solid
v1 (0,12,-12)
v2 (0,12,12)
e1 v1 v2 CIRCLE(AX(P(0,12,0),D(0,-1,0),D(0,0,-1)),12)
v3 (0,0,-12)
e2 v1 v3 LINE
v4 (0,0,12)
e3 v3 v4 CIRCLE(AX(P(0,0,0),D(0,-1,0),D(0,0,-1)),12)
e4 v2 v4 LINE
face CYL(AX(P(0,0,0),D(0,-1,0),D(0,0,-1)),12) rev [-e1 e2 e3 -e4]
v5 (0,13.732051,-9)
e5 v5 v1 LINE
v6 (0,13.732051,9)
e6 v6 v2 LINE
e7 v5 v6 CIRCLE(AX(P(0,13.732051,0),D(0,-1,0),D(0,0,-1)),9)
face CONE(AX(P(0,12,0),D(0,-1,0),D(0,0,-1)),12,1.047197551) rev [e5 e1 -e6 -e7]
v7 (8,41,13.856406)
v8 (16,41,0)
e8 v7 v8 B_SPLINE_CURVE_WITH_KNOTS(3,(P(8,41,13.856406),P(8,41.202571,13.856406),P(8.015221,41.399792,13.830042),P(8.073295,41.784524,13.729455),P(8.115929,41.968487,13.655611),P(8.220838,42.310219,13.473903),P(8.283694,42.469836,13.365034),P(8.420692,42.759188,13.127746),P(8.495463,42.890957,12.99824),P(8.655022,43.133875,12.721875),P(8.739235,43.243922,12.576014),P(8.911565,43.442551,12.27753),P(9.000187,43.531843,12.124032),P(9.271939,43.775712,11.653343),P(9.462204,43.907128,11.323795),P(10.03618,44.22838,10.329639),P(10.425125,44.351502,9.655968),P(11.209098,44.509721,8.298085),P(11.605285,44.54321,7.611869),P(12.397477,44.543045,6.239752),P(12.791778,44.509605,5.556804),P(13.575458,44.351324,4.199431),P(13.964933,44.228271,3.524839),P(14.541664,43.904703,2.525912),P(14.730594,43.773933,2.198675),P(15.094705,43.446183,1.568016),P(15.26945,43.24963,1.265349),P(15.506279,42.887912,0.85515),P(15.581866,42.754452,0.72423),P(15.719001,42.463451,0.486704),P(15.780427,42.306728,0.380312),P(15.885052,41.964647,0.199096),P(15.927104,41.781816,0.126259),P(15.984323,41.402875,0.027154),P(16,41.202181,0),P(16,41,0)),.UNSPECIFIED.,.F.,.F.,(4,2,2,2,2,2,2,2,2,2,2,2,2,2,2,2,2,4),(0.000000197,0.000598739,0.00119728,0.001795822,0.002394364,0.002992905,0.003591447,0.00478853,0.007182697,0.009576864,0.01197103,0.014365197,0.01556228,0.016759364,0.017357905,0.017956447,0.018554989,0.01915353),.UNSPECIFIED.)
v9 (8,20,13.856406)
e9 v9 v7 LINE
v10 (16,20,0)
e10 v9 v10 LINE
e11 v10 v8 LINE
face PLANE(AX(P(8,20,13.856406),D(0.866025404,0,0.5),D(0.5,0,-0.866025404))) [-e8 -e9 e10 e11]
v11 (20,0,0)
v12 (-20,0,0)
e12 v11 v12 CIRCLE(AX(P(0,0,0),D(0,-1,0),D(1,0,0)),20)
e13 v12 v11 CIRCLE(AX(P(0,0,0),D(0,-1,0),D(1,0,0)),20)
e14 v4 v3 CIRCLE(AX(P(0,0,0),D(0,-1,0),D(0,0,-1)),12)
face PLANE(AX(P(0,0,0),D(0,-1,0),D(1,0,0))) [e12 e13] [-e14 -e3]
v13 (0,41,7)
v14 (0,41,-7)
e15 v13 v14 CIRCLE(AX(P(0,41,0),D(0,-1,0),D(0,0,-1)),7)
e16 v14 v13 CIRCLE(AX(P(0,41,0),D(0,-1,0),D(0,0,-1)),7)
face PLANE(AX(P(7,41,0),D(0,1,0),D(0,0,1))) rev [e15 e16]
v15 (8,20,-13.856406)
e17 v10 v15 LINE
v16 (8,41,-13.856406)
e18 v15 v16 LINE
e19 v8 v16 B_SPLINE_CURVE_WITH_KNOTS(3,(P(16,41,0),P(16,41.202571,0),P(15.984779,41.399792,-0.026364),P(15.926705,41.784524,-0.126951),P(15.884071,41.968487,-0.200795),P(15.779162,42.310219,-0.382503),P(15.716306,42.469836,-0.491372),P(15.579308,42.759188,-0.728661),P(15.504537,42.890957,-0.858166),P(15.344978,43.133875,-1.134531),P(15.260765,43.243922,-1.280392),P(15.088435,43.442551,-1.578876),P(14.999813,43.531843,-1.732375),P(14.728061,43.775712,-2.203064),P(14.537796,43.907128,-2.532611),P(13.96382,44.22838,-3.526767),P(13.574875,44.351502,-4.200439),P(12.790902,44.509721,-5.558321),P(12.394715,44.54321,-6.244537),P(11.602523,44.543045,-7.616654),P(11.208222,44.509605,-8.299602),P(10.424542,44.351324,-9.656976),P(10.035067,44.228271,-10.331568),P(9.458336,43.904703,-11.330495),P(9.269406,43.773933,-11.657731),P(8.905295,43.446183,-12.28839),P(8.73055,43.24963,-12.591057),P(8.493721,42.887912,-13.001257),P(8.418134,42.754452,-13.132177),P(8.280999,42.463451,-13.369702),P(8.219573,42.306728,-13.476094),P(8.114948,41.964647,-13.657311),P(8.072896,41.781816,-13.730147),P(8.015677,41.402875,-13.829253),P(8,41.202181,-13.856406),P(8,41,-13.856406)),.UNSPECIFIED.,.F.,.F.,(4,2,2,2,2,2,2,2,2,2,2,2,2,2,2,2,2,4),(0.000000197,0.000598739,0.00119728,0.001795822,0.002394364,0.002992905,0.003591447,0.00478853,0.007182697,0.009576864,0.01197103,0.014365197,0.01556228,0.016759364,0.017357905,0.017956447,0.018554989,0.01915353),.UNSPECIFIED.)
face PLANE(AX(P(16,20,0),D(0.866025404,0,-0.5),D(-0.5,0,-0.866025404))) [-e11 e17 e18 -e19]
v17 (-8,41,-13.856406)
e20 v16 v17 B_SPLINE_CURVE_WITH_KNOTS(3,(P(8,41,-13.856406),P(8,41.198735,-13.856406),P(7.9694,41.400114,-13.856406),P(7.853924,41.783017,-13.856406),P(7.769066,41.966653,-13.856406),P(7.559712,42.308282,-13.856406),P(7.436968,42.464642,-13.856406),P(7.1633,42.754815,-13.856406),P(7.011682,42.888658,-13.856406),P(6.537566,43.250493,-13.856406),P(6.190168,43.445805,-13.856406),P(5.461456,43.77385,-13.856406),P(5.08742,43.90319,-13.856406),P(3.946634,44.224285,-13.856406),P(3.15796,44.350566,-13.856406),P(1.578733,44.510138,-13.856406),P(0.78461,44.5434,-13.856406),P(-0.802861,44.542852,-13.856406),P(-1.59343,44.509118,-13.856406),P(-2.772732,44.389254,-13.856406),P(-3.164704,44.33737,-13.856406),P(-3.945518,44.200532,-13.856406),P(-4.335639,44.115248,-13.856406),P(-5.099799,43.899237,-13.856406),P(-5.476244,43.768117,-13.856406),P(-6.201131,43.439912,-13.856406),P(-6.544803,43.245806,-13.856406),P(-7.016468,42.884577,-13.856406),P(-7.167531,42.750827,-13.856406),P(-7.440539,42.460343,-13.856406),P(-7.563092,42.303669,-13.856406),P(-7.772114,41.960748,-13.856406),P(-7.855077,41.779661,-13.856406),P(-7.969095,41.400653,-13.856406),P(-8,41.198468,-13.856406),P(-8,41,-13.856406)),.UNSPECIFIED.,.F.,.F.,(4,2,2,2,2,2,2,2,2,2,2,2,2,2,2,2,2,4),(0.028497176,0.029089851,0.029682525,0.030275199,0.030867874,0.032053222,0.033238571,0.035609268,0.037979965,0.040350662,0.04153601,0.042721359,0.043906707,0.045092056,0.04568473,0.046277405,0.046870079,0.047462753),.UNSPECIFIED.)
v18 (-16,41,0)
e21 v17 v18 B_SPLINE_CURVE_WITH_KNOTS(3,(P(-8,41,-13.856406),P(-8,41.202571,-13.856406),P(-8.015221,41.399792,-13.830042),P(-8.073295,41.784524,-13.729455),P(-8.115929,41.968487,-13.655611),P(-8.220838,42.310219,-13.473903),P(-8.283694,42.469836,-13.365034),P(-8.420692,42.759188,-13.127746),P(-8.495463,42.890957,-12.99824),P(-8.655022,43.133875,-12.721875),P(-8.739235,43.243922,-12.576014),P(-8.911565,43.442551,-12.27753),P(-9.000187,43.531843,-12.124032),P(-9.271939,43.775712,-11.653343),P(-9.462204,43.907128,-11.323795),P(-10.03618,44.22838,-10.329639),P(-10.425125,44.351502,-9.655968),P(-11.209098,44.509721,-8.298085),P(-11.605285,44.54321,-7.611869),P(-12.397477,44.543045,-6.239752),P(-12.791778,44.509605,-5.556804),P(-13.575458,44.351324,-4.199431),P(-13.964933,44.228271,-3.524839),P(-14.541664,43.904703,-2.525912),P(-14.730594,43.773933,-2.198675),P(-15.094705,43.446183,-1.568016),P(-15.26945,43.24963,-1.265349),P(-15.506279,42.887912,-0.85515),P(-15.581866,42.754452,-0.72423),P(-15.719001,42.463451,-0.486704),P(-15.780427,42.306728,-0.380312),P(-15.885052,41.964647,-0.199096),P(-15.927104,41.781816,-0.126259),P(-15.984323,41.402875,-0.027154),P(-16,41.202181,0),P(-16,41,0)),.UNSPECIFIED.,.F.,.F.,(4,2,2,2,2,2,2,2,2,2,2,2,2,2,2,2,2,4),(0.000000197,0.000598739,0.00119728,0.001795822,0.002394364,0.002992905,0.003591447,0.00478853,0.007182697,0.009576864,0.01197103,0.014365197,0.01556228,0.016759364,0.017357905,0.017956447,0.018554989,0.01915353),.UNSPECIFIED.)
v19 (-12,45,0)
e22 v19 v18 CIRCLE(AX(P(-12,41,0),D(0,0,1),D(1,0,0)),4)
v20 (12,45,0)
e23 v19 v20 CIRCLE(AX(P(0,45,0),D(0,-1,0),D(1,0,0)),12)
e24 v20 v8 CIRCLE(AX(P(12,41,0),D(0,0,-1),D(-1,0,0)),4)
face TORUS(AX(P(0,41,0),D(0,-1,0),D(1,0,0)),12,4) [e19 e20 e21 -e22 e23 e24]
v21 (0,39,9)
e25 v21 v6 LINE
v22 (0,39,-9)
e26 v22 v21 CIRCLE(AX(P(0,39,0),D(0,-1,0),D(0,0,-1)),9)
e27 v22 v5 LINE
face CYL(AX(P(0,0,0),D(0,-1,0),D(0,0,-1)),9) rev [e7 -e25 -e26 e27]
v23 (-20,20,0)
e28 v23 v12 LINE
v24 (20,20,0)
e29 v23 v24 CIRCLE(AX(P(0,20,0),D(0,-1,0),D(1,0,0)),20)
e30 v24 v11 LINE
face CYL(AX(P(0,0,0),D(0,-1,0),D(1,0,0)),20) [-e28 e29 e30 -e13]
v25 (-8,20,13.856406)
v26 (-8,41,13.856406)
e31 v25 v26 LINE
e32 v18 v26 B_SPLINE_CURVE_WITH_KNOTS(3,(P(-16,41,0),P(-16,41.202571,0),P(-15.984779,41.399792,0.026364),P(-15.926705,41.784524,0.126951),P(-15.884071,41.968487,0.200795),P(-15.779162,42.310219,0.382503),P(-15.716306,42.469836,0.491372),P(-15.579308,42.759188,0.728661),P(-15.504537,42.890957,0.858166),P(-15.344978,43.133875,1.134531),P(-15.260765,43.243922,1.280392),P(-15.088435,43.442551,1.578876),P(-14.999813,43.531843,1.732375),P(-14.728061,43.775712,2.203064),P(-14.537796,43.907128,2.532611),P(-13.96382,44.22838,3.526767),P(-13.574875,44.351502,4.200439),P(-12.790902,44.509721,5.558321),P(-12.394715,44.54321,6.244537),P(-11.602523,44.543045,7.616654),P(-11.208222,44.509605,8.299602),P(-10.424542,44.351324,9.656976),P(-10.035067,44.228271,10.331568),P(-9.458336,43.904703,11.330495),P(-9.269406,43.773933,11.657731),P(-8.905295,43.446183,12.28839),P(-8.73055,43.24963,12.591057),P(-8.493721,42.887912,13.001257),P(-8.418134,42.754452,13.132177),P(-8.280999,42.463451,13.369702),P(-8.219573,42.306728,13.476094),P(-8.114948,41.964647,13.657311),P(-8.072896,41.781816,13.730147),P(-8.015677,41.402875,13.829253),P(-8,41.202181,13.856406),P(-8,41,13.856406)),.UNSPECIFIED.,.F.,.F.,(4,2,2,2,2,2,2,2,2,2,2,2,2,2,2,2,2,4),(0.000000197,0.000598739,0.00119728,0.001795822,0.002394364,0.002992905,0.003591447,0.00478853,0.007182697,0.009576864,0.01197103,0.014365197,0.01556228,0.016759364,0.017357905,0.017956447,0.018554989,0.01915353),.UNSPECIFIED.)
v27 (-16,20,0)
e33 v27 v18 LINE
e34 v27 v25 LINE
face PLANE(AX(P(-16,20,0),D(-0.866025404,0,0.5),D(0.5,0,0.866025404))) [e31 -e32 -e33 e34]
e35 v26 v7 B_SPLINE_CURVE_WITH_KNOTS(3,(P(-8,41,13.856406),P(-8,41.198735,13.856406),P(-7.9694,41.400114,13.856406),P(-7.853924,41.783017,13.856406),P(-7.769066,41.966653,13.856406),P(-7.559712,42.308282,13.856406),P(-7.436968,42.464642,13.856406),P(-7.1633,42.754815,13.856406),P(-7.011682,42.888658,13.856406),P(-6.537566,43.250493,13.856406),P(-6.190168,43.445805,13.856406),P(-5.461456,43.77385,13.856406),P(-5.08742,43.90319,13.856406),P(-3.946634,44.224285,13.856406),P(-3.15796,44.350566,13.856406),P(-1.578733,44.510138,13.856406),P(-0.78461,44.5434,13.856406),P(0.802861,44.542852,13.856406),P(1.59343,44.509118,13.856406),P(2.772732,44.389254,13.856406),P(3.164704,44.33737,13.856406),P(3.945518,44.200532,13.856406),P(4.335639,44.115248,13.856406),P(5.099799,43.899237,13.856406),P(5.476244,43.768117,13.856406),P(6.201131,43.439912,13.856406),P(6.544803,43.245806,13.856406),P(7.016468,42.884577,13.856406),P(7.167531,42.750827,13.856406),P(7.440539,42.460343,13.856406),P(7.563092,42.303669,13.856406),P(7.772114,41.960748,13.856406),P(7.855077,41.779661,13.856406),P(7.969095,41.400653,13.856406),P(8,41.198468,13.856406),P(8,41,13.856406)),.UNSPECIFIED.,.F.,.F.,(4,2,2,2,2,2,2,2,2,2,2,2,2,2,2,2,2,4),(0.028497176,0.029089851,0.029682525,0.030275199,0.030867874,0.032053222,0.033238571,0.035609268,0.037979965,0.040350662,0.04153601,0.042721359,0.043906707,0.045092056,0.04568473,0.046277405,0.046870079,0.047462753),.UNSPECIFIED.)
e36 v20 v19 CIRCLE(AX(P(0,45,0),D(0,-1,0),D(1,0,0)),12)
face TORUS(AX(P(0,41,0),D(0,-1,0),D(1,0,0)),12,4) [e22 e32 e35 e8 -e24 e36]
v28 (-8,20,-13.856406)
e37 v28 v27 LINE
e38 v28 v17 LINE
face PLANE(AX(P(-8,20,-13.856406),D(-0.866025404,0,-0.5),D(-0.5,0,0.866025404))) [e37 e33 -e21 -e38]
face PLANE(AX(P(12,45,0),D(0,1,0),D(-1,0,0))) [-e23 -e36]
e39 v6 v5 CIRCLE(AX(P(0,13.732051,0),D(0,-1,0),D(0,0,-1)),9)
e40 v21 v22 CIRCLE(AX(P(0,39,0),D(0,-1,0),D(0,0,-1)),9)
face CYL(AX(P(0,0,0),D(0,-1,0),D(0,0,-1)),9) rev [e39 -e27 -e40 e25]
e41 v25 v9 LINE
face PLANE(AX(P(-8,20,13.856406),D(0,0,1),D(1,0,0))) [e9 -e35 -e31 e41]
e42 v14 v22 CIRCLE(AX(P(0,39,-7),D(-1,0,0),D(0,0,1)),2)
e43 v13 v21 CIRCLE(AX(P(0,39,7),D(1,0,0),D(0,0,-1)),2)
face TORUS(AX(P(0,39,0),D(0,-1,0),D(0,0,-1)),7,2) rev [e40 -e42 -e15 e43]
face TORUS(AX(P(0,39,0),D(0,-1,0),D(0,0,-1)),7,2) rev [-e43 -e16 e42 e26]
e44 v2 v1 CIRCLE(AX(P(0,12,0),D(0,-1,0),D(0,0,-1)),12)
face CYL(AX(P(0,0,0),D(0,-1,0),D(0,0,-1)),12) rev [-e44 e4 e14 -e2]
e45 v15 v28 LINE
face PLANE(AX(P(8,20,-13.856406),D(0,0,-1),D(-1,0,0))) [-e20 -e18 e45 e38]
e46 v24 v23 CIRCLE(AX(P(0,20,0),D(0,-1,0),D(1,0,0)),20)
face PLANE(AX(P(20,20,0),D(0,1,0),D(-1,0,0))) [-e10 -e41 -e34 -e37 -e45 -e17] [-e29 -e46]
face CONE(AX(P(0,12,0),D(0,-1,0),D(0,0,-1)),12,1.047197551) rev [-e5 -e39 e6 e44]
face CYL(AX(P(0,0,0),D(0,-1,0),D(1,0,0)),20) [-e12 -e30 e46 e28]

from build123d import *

# Parameters (mm, degrees)
HEX_32AF_SKETCH_OUTSIDE_W = 56.456
HEX_32AF_SKETCH_OUTSIDE_H = 56.456
HEX_32AF_CUT_DEPTH        = 25


with BuildPart() as part:
    # Cap Profile Sketch → Cap Body Revolve (revolve)
    with BuildSketch(Plane.XY):
        with BuildLine():
            Line((0, 0), (20, 0))
            Line((20, 0), (20, 20))
            Line((20, 20), (16, 20))
            Line((16, 20), (16, 41))
            ThreePointArc((16, 41), (14.828427125, 43.828427125), (12, 45))
            Line((12, 45), (0, 45))
            Line((0, 45), (0, 0))
        make_face()
    revolve(axis=Axis((0, 0, 0), (0, 1, 0)))

    # Hex 32AF Sketch outside → Hex 32AF Cut (cut)
    with BuildSketch(Plane(origin=(0, 45, 0), x_dir=(1, 0, 0), z_dir=(0, 1, 0))):
        Rectangle(HEX_32AF_SKETCH_OUTSIDE_W, HEX_32AF_SKETCH_OUTSIDE_H)
        Polygon((8, 13.856406461), (-8, 13.856406461), (-16, 0), (-8, -13.856406461), (8, -13.856406461), (16, 0), align=None, mode=Mode.SUBTRACT)
    extrude(amount=-HEX_32AF_CUT_DEPTH, mode=Mode.SUBTRACT)

    # Hex Chamfer 30deg Sketch → Hex Top Chamfer 30deg (revolve, cut)
    with BuildSketch(Plane.XY, mode=Mode.PRIVATE) as hex_top_chamfer_30deg_sk:
        with BuildLine():
            Line((0, 0), (12, 0))
            Line((12, 0), (12, 12))
            Line((12, 12), (9, 13.732050808))
            Line((9, 13.732050808), (9, 39))
            ThreePointArc((9, 39), (8.414213562, 40.414213562), (7, 41))
            Line((7, 41), (0, 41))
            Line((0, 41), (0, 0))
        make_face()
    revolve(hex_top_chamfer_30deg_sk.sketch.rotate(Axis((0, 0, 0), (0, 1, 0)), 90), axis=Axis((0, 0, 0), (0, 1, 0)), mode=Mode.SUBTRACT)


solid = part.part
